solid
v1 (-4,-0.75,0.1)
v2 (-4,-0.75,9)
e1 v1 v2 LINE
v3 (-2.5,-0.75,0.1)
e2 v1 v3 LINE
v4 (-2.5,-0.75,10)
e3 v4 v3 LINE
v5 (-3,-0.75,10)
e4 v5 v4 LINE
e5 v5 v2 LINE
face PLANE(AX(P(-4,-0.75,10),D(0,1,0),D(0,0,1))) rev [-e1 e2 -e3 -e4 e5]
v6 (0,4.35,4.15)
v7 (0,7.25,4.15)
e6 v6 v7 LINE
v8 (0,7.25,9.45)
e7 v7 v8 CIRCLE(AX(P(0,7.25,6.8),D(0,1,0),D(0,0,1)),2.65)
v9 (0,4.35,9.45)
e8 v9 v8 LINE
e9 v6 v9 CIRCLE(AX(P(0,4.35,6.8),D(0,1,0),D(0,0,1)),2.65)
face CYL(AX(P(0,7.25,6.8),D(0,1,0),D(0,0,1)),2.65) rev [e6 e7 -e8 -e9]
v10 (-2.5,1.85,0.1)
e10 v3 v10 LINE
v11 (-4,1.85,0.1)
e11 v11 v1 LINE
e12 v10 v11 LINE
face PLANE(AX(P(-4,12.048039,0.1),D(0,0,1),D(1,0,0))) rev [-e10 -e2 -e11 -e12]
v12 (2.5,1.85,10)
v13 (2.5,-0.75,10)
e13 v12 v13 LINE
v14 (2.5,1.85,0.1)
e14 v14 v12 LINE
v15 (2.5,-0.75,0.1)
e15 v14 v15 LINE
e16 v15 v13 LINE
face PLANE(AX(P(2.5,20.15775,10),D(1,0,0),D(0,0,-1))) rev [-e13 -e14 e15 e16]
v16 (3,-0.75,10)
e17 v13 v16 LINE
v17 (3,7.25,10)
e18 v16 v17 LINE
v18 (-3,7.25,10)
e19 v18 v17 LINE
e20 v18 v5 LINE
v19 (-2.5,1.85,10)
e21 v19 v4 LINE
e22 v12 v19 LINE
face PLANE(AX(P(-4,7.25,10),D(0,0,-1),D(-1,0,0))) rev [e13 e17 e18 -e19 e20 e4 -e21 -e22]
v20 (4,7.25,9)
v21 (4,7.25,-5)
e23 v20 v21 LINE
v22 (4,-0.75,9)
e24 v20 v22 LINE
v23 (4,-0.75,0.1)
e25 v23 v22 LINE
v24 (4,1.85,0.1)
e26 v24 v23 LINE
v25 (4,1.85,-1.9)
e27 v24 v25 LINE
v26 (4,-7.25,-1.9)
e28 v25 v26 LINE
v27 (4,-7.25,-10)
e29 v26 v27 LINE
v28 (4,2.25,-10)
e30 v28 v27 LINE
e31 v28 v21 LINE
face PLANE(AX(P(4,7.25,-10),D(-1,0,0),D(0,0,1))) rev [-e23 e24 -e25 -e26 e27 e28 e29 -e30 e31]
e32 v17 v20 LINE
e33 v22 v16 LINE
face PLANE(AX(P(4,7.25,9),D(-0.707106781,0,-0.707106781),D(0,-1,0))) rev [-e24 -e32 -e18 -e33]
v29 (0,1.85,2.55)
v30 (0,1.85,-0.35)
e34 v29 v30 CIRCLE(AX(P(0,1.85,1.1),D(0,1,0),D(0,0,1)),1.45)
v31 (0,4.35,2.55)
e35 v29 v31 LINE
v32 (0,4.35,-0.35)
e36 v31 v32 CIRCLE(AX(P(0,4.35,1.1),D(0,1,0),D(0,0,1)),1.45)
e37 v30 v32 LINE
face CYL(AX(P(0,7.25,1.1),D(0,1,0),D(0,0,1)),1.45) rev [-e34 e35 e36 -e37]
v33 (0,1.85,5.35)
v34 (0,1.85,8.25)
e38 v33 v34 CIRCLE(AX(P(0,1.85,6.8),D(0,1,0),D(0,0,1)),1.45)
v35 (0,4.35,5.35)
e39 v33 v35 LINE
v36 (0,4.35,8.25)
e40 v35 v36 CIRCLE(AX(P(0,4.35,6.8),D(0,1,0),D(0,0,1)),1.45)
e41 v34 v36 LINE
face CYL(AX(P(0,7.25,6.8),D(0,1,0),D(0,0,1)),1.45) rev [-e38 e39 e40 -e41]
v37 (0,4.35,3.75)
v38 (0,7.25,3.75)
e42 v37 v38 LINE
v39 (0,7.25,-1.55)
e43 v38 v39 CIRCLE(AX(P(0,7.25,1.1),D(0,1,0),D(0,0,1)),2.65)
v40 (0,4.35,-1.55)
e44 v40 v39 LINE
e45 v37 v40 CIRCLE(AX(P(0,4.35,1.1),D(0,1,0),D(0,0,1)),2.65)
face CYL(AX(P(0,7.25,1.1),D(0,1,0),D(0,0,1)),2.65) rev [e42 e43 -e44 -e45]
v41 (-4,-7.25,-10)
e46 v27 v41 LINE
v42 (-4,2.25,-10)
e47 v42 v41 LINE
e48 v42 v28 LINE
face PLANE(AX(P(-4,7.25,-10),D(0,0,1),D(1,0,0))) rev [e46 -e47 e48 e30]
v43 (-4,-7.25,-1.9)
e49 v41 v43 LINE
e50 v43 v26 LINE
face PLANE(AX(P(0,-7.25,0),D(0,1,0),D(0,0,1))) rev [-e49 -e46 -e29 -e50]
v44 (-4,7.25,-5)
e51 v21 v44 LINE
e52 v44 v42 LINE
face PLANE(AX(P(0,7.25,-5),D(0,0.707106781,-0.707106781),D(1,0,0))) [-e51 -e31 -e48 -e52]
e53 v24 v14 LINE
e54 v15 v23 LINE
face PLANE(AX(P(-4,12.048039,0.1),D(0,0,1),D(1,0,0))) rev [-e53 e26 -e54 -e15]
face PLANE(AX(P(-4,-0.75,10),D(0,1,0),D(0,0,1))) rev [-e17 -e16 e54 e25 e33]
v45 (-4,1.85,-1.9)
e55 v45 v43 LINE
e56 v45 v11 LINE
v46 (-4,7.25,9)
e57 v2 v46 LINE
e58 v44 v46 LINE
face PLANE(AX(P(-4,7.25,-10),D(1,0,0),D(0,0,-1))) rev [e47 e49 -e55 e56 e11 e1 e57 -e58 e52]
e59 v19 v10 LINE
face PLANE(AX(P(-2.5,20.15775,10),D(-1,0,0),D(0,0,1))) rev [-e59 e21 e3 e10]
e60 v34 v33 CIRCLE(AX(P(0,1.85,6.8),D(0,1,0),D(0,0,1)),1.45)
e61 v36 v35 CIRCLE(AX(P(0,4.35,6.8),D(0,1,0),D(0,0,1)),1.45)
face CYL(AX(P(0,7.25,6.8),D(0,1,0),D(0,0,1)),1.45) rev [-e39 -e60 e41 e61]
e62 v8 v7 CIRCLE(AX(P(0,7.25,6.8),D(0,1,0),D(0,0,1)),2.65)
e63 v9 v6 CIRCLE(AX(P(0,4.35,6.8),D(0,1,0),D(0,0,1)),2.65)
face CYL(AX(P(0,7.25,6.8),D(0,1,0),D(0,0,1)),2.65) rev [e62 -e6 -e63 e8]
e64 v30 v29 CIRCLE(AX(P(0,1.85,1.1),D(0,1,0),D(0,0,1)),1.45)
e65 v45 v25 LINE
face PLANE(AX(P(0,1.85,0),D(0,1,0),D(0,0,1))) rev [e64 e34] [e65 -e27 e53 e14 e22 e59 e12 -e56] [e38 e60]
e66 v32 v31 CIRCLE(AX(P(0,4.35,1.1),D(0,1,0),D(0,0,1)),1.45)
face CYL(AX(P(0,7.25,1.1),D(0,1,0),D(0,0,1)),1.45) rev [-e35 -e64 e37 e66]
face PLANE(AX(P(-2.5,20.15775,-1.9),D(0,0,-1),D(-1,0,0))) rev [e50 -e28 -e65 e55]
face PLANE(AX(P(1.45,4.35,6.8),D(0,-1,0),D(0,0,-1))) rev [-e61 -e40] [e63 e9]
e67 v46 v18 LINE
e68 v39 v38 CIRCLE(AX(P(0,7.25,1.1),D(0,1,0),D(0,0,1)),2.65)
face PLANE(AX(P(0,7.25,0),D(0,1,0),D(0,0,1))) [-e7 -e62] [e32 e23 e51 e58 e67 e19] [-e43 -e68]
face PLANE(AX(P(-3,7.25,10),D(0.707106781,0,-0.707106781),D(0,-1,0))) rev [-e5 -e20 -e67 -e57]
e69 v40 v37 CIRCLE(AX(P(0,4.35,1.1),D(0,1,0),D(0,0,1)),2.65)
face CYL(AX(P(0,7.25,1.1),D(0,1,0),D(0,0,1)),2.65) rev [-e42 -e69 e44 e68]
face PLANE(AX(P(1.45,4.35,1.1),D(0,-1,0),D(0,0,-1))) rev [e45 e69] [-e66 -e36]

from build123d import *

# Parameters (mm, degrees)
SKETCH1_W                                            = 8
SKETCH1_H                                            = 20
BOSS_EXTRUDE1_DEPTH                                  = 7.25
SKETCH2_W                                            = 5
SKETCH2_H                                            = 11.9
CUT_EXTRUDE1_DEPTH                                   = 9.1
CBORE_FOR_M2_5_HEX_SOCKET_HEAD_CAP_SCREW_D           = 2.9
CBORE_FOR_M2_5_HEX_SOCKET_HEAD_CAP_SCREW_CBORE_D     = 5.3
CBORE_FOR_M2_5_HEX_SOCKET_HEAD_CAP_SCREW_CBORE_DEPTH = 2.9
SKETCH7_W                                            = 11.4
SKETCH7_H                                            = 6.5
CUT_EXTRUDE3_DEPTH                                   = 15.716062653
CHAMFER1_SIZE                                        = 1
CHAMFER2_SIZE                                        = 5
CUT_EXTRUDE4_DEPTH                                   = 9.1


with BuildPart() as part:
    # Sketch1 → Boss-Extrude1 (new, symmetric)
    with BuildSketch(Plane(origin=(0, 0, 0), x_dir=(1, 0, 0), z_dir=(0, 1, 0))):
        Rectangle(SKETCH1_W, SKETCH1_H)
    extrude(amount=BOSS_EXTRUDE1_DEPTH, both=True)

    # Sketch2 → Cut-Extrude1 (cut)
    with BuildSketch(Plane.XZ.offset(7.25)):
        with Locations((0, 4.05)):
            Rectangle(SKETCH2_W, SKETCH2_H)
    extrude(amount=-CUT_EXTRUDE1_DEPTH, mode=Mode.SUBTRACT)

    # CBORE for M2.5 Hex Socket Head Cap Screw2 (through all)
    with Locations(Plane(origin=(0, 7.25, 0), x_dir=(1, 0, 0), z_dir=(0, 1, 0))):
        with Locations((0, -6.8), (0, -1.1)):
            CounterBoreHole(CBORE_FOR_M2_5_HEX_SOCKET_HEAD_CAP_SCREW_D / 2, CBORE_FOR_M2_5_HEX_SOCKET_HEAD_CAP_SCREW_CBORE_D / 2, CBORE_FOR_M2_5_HEX_SOCKET_HEAD_CAP_SCREW_CBORE_DEPTH)

    # Sketch7 → Cut-Extrude3 (cut, through all)
    with BuildSketch(Plane(origin=(4, 0, 0), x_dir=(0, 0, -1), z_dir=(1, 0, 0))):
        with Locations((-4.3, -4)):
            Rectangle(SKETCH7_W, SKETCH7_H)
    extrude(amount=-CUT_EXTRUDE3_DEPTH, mode=Mode.SUBTRACT)

    # Chamfer1
    chamfer1_edges = [part.edges().sort_by_distance(p)[0] for p in [
        (4, 3.25, 10),
        (-4, 3.25, 10),
    ]]
    chamfer(chamfer1_edges, length=CHAMFER1_SIZE)

    # Chamfer2
    chamfer2_edges = [part.edges().sort_by_distance(p)[0] for p in [
        (0, 7.25, -10),
    ]]
    chamfer(chamfer2_edges, length=CHAMFER2_SIZE)

    # Sketch6 → Cut-Extrude4 (cut)
    with BuildSketch(Plane.XZ.offset(7.25)):
        with BuildLine():
            Line((-4, 0.1), (4, 0.1))
            ThreePointArc((4, 0.1), (5, -0.9), (4, -1.9))
            Line((4, -1.9), (-4, -1.9))
            ThreePointArc((-4, -1.9), (-5, -0.9), (-4, 0.1))
        make_face()
    extrude(amount=-CUT_EXTRUDE4_DEPTH, mode=Mode.SUBTRACT)


solid = part.part
